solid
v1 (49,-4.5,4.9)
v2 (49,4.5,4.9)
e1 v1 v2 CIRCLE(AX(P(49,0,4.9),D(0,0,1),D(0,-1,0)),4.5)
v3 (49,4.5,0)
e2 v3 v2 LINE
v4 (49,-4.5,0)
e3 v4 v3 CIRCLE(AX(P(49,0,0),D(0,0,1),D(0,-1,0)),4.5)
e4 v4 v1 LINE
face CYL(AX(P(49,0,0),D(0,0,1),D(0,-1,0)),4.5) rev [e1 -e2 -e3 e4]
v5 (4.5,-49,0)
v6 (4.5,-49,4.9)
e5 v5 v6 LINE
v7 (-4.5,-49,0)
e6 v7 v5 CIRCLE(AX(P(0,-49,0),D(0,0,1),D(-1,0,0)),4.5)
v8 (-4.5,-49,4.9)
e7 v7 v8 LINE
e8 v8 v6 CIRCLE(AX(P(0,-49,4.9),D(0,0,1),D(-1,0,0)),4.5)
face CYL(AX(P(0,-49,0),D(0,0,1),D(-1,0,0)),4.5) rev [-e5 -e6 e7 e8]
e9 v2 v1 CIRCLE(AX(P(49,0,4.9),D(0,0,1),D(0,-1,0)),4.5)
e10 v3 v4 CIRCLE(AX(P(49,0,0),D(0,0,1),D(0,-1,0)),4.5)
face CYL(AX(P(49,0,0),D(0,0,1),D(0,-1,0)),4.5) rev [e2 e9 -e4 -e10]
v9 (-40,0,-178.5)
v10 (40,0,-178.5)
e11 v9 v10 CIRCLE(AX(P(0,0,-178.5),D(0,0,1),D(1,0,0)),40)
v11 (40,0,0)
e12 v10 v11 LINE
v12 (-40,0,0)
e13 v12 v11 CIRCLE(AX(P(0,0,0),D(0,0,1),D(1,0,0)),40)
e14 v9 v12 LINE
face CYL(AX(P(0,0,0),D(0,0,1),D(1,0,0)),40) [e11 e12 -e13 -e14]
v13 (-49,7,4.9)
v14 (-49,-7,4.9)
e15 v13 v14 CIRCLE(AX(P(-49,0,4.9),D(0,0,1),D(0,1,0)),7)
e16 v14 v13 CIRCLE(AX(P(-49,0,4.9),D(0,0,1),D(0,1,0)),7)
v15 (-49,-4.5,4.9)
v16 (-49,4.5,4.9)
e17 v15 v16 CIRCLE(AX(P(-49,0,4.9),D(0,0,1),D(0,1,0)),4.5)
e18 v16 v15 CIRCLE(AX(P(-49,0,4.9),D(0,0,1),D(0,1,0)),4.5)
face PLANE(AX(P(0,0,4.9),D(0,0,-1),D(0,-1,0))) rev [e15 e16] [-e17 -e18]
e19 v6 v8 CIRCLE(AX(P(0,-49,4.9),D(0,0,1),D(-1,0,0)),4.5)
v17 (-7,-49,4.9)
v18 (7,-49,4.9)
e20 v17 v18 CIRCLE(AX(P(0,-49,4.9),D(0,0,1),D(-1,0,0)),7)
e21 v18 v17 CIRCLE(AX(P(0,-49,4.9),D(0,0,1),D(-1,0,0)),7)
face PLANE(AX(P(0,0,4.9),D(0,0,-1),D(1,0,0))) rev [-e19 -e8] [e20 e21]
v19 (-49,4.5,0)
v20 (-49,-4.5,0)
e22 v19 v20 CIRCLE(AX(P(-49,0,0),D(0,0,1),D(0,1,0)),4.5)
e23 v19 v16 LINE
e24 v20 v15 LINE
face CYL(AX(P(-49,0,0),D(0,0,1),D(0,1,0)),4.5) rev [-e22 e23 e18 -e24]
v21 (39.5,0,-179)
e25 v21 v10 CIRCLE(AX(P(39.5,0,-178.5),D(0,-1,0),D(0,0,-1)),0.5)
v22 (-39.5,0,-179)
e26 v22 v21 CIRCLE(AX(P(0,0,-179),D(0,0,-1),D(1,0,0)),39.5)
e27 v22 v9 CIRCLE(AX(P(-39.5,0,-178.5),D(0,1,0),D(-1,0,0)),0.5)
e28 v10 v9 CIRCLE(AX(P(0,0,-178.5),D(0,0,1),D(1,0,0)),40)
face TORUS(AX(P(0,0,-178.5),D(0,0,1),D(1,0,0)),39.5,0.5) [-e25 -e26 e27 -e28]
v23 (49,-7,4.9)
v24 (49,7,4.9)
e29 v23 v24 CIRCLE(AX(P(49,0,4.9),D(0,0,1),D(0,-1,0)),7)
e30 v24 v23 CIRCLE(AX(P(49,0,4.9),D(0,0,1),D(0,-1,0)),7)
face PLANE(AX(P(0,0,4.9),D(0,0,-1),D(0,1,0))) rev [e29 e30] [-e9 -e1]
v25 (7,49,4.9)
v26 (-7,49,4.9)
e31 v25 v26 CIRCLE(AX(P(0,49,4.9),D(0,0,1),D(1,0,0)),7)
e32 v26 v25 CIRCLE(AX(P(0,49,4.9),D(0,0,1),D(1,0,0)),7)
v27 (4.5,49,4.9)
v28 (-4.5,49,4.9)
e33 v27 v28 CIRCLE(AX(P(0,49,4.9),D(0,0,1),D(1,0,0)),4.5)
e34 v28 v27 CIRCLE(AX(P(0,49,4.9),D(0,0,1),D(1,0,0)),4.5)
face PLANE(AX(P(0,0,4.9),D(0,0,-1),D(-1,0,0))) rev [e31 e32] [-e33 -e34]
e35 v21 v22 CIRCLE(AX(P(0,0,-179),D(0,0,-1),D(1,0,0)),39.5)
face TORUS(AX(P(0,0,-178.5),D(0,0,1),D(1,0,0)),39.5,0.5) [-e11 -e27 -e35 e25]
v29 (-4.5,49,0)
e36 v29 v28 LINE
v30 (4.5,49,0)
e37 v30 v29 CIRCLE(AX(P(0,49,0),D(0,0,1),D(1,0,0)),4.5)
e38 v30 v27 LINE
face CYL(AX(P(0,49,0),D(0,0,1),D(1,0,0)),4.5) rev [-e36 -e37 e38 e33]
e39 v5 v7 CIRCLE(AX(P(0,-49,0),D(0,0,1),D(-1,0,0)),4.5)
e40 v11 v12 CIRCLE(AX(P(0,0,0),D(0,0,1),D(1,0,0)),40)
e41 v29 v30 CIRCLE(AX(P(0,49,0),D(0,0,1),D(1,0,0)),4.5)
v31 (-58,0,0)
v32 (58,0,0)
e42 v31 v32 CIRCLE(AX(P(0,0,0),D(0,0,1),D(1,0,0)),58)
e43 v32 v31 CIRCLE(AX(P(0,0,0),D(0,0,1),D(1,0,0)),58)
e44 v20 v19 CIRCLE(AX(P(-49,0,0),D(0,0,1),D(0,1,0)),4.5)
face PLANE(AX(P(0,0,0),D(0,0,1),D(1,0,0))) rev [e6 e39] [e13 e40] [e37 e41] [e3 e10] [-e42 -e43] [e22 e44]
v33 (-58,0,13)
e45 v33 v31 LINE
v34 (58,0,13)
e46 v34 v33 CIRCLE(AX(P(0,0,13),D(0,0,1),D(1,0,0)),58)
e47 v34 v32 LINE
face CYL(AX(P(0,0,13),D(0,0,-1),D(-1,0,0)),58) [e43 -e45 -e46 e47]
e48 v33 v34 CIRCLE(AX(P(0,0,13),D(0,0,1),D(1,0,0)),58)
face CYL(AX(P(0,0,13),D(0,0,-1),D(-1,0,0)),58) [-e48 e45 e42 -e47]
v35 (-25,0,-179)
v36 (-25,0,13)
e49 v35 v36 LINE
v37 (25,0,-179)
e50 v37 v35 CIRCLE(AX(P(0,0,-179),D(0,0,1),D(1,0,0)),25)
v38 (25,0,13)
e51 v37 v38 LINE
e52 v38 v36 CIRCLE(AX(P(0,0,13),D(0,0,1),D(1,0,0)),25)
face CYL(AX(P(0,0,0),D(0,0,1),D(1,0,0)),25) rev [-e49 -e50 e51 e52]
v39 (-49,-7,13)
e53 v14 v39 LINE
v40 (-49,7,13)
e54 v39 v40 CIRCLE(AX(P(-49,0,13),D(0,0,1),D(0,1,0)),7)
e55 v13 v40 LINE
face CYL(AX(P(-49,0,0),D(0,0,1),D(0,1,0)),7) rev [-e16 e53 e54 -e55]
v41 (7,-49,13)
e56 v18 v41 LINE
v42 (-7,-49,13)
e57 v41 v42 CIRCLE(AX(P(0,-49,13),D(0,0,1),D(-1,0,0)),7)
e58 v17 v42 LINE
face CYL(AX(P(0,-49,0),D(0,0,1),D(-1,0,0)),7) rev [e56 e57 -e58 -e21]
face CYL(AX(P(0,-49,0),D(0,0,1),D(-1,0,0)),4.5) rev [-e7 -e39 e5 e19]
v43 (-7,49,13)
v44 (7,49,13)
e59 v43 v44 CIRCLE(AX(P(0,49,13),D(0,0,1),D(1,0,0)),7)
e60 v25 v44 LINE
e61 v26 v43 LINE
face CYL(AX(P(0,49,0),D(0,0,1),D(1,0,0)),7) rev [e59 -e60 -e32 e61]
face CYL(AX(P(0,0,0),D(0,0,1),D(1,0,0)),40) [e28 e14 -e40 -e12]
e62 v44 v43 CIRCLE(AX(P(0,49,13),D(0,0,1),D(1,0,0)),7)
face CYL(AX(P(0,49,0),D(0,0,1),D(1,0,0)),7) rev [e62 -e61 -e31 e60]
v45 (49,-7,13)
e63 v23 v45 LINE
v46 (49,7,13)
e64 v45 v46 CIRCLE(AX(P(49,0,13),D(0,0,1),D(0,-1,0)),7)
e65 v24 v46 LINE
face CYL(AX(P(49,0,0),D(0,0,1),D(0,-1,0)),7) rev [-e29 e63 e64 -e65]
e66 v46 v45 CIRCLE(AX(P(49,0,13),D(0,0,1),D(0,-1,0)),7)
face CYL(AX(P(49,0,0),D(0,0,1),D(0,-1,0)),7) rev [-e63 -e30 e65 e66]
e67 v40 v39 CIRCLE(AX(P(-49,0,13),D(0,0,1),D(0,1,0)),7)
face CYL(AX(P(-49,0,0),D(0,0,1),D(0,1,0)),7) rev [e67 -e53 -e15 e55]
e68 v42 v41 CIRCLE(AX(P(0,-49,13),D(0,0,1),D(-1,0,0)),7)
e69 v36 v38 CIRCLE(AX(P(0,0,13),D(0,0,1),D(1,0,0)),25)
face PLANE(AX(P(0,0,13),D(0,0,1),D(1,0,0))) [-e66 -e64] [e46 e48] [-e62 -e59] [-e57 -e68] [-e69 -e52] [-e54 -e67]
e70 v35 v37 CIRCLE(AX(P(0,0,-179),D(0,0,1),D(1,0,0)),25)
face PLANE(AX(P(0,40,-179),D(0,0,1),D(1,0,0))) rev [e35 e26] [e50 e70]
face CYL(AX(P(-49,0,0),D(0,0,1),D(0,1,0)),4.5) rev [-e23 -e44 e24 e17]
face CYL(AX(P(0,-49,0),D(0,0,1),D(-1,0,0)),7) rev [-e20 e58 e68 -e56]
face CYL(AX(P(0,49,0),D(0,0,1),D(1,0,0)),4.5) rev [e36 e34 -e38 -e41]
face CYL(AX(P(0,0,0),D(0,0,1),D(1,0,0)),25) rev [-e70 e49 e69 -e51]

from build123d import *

# Parameters (mm, degrees)
SKETCH_1_W               = 179
SKETCH_1_H               = 15
FILLET_1_R               = 0.5
EXTRUDE_START            = 13
SKETCH_2_R               = 58
SKETCH_2_R_2             = 25
EXTRUDE_1_DEPTH          = 13
SKETCH_3_W               = 8.1
SKETCH_3_H               = 7
SKETCH_3_W_2             = 4.9
SKETCH_3_H_2             = 4.5
PATTERN_CIRCULAR_1_COUNT = 4


with BuildPart() as part:
    # 草图1 → 旋转1 (revolve)
    with BuildSketch(Plane(origin=(0, 0, 0), x_dir=(0, 0, -1), z_dir=(1, 0, 0)), mode=Mode.PRIVATE) as revolve_1_sk:
        with Locations((89.5, 32.5)):
            Rectangle(SKETCH_1_W, SKETCH_1_H)
    revolve(revolve_1_sk.sketch.rotate(Axis((0, 0, 0), (0, 0, -1)), 90), axis=Axis((0, 0, 0), (0, 0, -1)))

    # 圆角1
    fillet_1_edges = [part.edges().sort_by_distance(p)[0] for p in [
        (-40, 0, -179),
    ]]
    fillet(fillet_1_edges, radius=FILLET_1_R)

    # 草图2 → 凸台-拉伸1 (add)
    with BuildSketch(Plane.XY.offset(EXTRUDE_START)):
        with Locations(Location((0, 0, 0), (0, 0, 180))):
            Circle(SKETCH_2_R)
        Circle(SKETCH_2_R_2, mode=Mode.SUBTRACT)
    extrude(amount=-EXTRUDE_1_DEPTH)

    # 草图3 → 切除-旋转1 (revolve, cut)
    with BuildSketch(Plane(origin=(0, 0, 0), x_dir=(0, 0, -1), z_dir=(1, 0, 0)), mode=Mode.PRIVATE) as cut_revolve_1_sk:
        with Locations((-8.95, 52.5)):
            Rectangle(SKETCH_3_W, SKETCH_3_H)
        Polygon((-4.9, 56), (-13, 56), (-13, 49), (-4.9, 49), (-4.9, 53.5), align=None)
        with Locations((-2.45, 51.25)):
            Rectangle(SKETCH_3_W_2, SKETCH_3_H_2)
    cut_revolve_1 = revolve(cut_revolve_1_sk.sketch.rotate(Axis((0, 49, 0), (0, 0, -1)), 90), axis=Axis((0, 49, 0), (0, 0, -1)), mode=Mode.SUBTRACT)

    # 阵列(圆周)1: 切除-旋转1 ×4 about axis
    pattern_circular_1_axis = Axis((0, 0, 0), (0, 0, 1))
    for i in range(1, PATTERN_CIRCULAR_1_COUNT):
        add(cut_revolve_1.rotate(pattern_circular_1_axis, i * 360 / PATTERN_CIRCULAR_1_COUNT), mode=Mode.SUBTRACT)


solid = part.part
